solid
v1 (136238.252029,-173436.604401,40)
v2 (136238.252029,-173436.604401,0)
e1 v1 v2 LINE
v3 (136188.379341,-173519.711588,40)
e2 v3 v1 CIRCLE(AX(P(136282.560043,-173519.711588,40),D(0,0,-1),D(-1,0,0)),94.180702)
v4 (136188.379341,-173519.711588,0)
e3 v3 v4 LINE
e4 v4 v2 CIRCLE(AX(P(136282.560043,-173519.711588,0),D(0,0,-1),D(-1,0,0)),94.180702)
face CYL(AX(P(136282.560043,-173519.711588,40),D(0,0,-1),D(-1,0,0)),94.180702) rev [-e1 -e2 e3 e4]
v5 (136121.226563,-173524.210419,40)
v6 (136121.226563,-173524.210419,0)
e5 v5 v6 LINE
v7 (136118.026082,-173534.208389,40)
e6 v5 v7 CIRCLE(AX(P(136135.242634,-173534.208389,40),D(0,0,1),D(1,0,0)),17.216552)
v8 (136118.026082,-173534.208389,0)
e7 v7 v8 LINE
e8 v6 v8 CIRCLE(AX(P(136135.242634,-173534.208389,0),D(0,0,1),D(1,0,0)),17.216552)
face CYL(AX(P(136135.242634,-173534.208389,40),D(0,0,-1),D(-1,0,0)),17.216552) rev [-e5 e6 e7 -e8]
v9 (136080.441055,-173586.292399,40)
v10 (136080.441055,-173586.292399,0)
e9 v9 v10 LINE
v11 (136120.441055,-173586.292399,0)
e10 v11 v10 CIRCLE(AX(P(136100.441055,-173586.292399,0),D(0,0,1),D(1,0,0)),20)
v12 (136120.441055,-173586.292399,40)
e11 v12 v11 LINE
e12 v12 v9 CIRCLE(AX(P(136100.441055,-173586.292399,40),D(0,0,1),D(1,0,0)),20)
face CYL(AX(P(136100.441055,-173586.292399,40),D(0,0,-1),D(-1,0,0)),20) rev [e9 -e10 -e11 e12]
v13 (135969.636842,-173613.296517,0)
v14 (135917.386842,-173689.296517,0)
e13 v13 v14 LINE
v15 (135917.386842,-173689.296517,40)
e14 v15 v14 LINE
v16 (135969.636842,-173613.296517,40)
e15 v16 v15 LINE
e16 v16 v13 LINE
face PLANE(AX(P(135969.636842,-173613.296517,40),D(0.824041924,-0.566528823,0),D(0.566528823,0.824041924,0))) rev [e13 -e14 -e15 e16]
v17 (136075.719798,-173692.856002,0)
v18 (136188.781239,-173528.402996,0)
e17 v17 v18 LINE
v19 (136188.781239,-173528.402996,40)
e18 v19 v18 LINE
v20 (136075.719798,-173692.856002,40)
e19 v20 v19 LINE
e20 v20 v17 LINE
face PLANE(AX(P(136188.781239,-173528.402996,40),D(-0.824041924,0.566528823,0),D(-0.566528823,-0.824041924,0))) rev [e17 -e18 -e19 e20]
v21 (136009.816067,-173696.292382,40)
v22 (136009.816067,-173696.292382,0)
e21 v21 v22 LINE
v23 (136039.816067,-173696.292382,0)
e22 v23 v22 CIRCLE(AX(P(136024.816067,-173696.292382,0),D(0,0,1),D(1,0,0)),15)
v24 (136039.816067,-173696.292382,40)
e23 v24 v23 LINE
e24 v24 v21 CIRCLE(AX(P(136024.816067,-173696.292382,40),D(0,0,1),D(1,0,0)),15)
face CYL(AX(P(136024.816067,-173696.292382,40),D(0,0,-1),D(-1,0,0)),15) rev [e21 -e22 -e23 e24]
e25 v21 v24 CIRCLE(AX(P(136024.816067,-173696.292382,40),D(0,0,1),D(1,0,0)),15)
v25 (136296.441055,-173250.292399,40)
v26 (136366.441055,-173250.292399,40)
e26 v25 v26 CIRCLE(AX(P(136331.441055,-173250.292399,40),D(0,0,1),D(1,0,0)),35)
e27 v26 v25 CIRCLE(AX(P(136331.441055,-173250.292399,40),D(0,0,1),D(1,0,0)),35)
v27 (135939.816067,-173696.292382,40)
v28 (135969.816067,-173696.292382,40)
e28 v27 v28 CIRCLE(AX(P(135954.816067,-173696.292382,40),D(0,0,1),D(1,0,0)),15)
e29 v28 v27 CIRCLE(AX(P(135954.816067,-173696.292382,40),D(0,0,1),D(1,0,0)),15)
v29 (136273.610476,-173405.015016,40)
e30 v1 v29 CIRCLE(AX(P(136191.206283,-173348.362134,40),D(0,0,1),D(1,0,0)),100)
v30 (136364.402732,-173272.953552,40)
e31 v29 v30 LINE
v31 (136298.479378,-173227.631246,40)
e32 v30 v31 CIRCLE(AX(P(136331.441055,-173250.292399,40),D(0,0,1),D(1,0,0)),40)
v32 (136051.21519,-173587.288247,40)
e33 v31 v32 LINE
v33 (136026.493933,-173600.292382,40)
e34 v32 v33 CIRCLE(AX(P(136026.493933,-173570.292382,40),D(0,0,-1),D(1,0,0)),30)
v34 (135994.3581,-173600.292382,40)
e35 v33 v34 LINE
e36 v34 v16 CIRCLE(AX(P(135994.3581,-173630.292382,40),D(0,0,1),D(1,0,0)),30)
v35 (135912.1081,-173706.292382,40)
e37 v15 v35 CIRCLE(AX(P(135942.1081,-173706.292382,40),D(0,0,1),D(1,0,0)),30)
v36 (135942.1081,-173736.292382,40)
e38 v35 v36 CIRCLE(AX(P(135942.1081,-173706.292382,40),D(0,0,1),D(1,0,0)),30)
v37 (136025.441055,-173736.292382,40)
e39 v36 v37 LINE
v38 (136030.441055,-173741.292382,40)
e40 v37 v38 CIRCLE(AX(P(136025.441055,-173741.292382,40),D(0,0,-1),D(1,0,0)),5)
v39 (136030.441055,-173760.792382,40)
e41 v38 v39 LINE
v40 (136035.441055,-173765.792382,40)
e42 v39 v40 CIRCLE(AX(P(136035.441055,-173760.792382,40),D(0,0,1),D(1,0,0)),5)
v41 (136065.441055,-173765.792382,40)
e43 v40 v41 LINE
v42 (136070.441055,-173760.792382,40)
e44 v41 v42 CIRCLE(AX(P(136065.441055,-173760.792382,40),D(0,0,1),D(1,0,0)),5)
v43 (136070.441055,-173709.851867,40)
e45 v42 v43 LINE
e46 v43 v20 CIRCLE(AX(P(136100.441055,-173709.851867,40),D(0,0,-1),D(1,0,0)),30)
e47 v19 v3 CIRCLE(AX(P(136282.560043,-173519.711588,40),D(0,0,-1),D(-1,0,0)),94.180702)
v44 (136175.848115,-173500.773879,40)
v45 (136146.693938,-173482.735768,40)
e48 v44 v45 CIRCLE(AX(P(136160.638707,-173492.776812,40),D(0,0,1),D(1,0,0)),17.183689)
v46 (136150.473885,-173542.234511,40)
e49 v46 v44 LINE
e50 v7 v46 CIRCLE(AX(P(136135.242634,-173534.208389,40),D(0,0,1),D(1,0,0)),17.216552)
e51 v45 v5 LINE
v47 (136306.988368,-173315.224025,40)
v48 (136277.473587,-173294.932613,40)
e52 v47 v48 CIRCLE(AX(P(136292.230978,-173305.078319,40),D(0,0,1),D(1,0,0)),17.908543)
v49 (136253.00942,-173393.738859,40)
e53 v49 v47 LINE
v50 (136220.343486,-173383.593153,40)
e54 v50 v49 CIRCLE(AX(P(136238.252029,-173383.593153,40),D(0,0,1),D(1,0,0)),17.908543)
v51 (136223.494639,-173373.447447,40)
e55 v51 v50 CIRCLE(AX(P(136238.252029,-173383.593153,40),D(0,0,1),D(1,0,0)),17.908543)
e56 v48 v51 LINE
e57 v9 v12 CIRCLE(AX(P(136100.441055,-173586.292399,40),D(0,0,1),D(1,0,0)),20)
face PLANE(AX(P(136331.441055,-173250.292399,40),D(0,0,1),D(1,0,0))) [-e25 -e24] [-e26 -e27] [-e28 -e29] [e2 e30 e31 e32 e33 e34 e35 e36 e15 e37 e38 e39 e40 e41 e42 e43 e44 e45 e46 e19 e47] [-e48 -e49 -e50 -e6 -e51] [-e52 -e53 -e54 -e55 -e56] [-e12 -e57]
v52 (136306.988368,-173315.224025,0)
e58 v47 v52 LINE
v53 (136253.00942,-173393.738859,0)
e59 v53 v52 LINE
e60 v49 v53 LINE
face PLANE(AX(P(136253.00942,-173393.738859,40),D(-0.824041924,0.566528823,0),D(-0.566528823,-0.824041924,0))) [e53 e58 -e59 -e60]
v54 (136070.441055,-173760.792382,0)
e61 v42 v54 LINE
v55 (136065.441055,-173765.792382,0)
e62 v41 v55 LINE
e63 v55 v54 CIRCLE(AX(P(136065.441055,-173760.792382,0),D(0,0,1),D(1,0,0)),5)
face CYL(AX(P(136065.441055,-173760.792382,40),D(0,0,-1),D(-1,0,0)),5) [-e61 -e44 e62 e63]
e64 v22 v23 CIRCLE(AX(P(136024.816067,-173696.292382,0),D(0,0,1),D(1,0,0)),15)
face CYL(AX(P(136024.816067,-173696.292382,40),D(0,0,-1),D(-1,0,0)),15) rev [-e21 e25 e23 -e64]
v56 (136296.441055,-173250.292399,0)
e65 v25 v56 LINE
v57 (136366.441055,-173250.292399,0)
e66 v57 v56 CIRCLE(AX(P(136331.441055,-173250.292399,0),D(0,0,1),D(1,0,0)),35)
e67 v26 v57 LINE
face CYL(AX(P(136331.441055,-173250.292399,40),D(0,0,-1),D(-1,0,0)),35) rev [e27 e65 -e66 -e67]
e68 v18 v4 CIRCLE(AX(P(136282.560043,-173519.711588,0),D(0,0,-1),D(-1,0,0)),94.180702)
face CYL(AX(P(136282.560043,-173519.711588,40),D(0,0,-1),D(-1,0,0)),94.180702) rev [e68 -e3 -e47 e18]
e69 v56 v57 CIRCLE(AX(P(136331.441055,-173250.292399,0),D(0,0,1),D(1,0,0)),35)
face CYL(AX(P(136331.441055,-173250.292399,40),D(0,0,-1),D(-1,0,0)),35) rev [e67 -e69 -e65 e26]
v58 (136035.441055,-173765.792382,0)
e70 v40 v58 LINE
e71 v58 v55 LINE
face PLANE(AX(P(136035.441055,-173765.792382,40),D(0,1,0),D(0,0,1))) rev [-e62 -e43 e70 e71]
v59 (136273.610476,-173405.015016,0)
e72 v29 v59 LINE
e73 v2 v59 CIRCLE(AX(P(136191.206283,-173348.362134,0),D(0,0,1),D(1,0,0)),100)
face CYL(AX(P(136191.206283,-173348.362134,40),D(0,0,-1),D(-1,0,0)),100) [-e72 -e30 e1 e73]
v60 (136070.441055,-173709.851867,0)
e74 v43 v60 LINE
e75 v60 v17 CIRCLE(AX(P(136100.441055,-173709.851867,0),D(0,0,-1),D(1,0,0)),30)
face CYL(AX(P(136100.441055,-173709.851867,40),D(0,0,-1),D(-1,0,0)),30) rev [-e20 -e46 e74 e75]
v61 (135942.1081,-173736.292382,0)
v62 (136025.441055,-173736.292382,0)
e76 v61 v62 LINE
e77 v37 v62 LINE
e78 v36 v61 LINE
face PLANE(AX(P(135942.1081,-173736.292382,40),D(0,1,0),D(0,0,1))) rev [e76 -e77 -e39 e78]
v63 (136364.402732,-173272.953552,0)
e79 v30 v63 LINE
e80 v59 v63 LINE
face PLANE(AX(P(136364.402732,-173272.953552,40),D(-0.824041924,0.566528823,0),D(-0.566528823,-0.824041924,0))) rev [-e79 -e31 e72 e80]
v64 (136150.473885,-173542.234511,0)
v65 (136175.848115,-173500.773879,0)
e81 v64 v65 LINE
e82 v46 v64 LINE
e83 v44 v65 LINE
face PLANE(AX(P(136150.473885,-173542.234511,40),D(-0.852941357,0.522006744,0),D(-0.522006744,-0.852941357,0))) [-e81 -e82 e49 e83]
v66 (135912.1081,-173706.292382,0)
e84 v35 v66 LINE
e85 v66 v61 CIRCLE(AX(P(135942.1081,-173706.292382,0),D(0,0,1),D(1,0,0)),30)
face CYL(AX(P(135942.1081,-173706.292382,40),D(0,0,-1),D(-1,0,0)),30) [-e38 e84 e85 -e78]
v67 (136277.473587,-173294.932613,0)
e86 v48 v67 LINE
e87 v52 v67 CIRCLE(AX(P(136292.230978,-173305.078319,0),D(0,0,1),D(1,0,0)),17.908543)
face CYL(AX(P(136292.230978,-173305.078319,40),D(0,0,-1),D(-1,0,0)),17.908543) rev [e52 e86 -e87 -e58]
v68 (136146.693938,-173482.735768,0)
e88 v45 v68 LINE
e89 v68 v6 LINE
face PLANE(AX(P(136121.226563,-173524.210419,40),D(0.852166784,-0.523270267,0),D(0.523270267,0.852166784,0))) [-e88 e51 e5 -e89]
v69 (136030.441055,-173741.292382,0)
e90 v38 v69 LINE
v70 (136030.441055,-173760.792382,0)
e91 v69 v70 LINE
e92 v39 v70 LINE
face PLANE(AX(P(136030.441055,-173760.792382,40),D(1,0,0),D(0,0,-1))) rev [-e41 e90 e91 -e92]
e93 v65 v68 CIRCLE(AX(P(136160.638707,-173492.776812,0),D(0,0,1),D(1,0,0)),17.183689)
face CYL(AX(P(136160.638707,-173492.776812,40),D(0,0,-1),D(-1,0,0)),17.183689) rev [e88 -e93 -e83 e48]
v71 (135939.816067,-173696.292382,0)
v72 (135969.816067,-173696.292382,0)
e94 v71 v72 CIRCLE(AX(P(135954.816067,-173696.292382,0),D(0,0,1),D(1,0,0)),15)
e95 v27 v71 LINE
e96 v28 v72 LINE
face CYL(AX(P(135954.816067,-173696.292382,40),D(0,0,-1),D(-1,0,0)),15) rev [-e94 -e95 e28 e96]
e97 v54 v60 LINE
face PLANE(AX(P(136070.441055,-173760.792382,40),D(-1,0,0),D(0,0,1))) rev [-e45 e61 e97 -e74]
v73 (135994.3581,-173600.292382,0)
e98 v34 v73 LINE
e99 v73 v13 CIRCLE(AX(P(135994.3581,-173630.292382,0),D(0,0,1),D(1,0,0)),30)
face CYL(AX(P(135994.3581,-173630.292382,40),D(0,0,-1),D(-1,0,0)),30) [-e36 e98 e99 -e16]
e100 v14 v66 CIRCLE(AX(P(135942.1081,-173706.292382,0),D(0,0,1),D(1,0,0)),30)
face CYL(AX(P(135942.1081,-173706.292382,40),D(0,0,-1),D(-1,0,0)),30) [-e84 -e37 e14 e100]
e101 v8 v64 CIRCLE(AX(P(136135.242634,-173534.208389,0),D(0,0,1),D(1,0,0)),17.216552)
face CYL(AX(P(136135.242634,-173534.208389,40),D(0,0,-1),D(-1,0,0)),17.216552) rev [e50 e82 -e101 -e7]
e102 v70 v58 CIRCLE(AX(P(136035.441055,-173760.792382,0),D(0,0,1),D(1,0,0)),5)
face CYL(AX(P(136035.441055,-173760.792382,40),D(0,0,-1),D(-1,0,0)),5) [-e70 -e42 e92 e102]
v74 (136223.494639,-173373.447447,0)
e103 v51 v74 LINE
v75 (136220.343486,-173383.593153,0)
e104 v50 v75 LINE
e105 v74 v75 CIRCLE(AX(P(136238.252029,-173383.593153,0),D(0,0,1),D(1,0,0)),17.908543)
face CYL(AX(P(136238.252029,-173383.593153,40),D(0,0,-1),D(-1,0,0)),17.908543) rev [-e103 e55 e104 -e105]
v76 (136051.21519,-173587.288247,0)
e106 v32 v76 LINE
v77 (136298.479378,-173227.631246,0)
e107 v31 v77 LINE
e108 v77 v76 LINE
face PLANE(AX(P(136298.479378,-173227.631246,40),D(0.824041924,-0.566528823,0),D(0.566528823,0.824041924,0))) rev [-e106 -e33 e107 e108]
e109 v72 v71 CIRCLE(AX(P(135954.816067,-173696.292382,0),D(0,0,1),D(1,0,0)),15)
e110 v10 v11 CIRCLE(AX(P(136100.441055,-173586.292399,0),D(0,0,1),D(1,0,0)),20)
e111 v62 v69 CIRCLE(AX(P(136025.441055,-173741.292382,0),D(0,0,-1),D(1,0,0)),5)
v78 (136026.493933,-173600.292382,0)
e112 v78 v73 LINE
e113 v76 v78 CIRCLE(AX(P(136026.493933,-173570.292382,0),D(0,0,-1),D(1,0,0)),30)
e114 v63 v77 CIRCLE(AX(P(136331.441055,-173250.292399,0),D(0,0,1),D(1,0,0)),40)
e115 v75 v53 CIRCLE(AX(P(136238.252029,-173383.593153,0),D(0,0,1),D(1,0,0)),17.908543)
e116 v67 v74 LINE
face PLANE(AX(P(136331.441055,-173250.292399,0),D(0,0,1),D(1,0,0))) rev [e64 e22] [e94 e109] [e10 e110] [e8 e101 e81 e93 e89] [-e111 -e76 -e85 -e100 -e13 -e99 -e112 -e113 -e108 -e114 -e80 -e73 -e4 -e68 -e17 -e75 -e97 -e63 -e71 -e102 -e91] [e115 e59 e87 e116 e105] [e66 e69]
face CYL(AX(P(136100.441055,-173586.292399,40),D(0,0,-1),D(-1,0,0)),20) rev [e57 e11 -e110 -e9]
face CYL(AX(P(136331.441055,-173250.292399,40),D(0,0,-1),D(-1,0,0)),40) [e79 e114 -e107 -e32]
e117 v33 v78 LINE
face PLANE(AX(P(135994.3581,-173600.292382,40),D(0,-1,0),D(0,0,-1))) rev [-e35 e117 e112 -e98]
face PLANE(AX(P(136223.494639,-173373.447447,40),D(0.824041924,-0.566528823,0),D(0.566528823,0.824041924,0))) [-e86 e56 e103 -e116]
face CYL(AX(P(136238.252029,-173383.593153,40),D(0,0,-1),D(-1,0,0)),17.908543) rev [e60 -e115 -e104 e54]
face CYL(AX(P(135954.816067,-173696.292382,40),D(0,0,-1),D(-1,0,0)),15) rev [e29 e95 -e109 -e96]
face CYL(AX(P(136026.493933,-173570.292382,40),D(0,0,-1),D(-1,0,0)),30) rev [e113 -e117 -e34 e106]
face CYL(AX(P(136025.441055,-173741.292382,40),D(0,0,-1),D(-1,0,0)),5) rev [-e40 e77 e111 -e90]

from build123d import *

# Parameters (mm, degrees)
SKETCH1_R           = 15
SKETCH1_R_2         = 20
SKETCH1_R_3         = 35
BOSS_EXTRUDE1_DEPTH = 40


with BuildPart() as part:
    # Sketch1 → Boss-Extrude1 (new body)
    with BuildSketch(Plane.XY):
        with BuildLine():
            Line((136298.479378134, -173227.631246443), (136051.215190424, -173587.288246748))
            ThreePointArc((136051.215190424, -173587.288246748), (136040.460393586, -173596.843050045), (136026.493932699, -173600.292382063))
            Line((136026.493932699, -173600.292382063), (135994.358099543, -173600.292382063))
            ThreePointArc((135994.358099543, -173600.292382063), (135980.391638657, -173603.741714079), (135969.636841818, -173613.296517373))
            Line((135969.636841818, -173613.296517373), (135917.386841817, -173689.296517375))
            ThreePointArc((135917.386841817, -173689.296517375), (135915.557431558, -173720.258842949), (135942.10809954, -173736.292382064))
            Line((135942.10809954, -173736.292382064), (136025.44105537, -173736.292382064))
            ThreePointArc((136025.44105537, -173736.292382064), (136028.976589274, -173737.756848164), (136030.44105537, -173741.29238207))
            Line((136030.44105537, -173741.29238207), (136030.44105537, -173760.79238207))
            ThreePointArc((136030.44105537, -173760.79238207), (136031.905521462, -173764.327915975), (136035.441055367, -173765.79238207))
            Line((136035.441055367, -173765.79238207), (136065.44105537, -173765.79238207))
            ThreePointArc((136065.44105537, -173765.79238207), (136068.976589275, -173764.327915968), (136070.441055364, -173760.792382057))
            Line((136070.441055364, -173760.792382057), (136070.441055364, -173709.851867037))
            ThreePointArc((136070.441055364, -173709.851867037), (136071.791118787, -173700.953488864), (136075.71979764, -173692.856002351))
            Line((136075.71979764, -173692.856002351), (136188.781239342, -173528.402996239))
            ThreePointArc((136188.781239342, -173528.402996239), (136199.652035077, -173475.031986515), (136238.252029422, -173436.60440117))
            ThreePointArc((136238.252029422, -173436.60440117), (136257.830557919, -173422.935627875), (136273.610475811, -173405.01501592))
            Line((136273.610475811, -173405.01501592), (136364.402732332, -173272.953551889))
            ThreePointArc((136364.402732332, -173272.953551889), (136354.102207956, -173217.330722066), (136298.479378134, -173227.631246443))
        make_face()
        with Locations((136024.816066991, -173696.292382064)):
            Circle(SKETCH1_R, mode=Mode.SUBTRACT)
        with Locations((135954.816066991, -173696.292382064)):
            Circle(SKETCH1_R, mode=Mode.SUBTRACT)
        with Locations((136100.44105537, -173586.292398967)):
            Circle(SKETCH1_R_2, mode=Mode.SUBTRACT)
        with Locations((136331.44105537, -173250.292398967)):
            Circle(SKETCH1_R_3, mode=Mode.SUBTRACT)
        with BuildLine():
            Line((136121.226562597, -173524.21041858), (136146.693938197, -173482.735767799))
            ThreePointArc((136146.693938197, -173482.735767799), (136169.679901616, -173478.163942115), (136175.848114544, -173500.773879171))
            Line((136175.848114544, -173500.773879171), (136150.47388525, -173542.2345113))
            ThreePointArc((136150.47388525, -173542.2345113), (136126.210129016, -173548.865247662), (136121.226562597, -173524.21041858))
        make_face(mode=Mode.SUBTRACT)
        with BuildLine():
            Line((136223.494638872, -173373.447446962), (136277.473587055, -173294.932613241))
            ThreePointArc((136277.473587055, -173294.932613241), (136302.376683609, -173290.320928694), (136306.988368156, -173315.224025248))
            Line((136306.988368156, -173315.224025248), (136253.009419973, -173393.738858969))
            ThreePointArc((136253.009419973, -173393.738858969), (136228.106323419, -173398.350543516), (136223.494638872, -173373.447446962))
        make_face(mode=Mode.SUBTRACT)
    extrude(amount=BOSS_EXTRUDE1_DEPTH)


solid = part.part
